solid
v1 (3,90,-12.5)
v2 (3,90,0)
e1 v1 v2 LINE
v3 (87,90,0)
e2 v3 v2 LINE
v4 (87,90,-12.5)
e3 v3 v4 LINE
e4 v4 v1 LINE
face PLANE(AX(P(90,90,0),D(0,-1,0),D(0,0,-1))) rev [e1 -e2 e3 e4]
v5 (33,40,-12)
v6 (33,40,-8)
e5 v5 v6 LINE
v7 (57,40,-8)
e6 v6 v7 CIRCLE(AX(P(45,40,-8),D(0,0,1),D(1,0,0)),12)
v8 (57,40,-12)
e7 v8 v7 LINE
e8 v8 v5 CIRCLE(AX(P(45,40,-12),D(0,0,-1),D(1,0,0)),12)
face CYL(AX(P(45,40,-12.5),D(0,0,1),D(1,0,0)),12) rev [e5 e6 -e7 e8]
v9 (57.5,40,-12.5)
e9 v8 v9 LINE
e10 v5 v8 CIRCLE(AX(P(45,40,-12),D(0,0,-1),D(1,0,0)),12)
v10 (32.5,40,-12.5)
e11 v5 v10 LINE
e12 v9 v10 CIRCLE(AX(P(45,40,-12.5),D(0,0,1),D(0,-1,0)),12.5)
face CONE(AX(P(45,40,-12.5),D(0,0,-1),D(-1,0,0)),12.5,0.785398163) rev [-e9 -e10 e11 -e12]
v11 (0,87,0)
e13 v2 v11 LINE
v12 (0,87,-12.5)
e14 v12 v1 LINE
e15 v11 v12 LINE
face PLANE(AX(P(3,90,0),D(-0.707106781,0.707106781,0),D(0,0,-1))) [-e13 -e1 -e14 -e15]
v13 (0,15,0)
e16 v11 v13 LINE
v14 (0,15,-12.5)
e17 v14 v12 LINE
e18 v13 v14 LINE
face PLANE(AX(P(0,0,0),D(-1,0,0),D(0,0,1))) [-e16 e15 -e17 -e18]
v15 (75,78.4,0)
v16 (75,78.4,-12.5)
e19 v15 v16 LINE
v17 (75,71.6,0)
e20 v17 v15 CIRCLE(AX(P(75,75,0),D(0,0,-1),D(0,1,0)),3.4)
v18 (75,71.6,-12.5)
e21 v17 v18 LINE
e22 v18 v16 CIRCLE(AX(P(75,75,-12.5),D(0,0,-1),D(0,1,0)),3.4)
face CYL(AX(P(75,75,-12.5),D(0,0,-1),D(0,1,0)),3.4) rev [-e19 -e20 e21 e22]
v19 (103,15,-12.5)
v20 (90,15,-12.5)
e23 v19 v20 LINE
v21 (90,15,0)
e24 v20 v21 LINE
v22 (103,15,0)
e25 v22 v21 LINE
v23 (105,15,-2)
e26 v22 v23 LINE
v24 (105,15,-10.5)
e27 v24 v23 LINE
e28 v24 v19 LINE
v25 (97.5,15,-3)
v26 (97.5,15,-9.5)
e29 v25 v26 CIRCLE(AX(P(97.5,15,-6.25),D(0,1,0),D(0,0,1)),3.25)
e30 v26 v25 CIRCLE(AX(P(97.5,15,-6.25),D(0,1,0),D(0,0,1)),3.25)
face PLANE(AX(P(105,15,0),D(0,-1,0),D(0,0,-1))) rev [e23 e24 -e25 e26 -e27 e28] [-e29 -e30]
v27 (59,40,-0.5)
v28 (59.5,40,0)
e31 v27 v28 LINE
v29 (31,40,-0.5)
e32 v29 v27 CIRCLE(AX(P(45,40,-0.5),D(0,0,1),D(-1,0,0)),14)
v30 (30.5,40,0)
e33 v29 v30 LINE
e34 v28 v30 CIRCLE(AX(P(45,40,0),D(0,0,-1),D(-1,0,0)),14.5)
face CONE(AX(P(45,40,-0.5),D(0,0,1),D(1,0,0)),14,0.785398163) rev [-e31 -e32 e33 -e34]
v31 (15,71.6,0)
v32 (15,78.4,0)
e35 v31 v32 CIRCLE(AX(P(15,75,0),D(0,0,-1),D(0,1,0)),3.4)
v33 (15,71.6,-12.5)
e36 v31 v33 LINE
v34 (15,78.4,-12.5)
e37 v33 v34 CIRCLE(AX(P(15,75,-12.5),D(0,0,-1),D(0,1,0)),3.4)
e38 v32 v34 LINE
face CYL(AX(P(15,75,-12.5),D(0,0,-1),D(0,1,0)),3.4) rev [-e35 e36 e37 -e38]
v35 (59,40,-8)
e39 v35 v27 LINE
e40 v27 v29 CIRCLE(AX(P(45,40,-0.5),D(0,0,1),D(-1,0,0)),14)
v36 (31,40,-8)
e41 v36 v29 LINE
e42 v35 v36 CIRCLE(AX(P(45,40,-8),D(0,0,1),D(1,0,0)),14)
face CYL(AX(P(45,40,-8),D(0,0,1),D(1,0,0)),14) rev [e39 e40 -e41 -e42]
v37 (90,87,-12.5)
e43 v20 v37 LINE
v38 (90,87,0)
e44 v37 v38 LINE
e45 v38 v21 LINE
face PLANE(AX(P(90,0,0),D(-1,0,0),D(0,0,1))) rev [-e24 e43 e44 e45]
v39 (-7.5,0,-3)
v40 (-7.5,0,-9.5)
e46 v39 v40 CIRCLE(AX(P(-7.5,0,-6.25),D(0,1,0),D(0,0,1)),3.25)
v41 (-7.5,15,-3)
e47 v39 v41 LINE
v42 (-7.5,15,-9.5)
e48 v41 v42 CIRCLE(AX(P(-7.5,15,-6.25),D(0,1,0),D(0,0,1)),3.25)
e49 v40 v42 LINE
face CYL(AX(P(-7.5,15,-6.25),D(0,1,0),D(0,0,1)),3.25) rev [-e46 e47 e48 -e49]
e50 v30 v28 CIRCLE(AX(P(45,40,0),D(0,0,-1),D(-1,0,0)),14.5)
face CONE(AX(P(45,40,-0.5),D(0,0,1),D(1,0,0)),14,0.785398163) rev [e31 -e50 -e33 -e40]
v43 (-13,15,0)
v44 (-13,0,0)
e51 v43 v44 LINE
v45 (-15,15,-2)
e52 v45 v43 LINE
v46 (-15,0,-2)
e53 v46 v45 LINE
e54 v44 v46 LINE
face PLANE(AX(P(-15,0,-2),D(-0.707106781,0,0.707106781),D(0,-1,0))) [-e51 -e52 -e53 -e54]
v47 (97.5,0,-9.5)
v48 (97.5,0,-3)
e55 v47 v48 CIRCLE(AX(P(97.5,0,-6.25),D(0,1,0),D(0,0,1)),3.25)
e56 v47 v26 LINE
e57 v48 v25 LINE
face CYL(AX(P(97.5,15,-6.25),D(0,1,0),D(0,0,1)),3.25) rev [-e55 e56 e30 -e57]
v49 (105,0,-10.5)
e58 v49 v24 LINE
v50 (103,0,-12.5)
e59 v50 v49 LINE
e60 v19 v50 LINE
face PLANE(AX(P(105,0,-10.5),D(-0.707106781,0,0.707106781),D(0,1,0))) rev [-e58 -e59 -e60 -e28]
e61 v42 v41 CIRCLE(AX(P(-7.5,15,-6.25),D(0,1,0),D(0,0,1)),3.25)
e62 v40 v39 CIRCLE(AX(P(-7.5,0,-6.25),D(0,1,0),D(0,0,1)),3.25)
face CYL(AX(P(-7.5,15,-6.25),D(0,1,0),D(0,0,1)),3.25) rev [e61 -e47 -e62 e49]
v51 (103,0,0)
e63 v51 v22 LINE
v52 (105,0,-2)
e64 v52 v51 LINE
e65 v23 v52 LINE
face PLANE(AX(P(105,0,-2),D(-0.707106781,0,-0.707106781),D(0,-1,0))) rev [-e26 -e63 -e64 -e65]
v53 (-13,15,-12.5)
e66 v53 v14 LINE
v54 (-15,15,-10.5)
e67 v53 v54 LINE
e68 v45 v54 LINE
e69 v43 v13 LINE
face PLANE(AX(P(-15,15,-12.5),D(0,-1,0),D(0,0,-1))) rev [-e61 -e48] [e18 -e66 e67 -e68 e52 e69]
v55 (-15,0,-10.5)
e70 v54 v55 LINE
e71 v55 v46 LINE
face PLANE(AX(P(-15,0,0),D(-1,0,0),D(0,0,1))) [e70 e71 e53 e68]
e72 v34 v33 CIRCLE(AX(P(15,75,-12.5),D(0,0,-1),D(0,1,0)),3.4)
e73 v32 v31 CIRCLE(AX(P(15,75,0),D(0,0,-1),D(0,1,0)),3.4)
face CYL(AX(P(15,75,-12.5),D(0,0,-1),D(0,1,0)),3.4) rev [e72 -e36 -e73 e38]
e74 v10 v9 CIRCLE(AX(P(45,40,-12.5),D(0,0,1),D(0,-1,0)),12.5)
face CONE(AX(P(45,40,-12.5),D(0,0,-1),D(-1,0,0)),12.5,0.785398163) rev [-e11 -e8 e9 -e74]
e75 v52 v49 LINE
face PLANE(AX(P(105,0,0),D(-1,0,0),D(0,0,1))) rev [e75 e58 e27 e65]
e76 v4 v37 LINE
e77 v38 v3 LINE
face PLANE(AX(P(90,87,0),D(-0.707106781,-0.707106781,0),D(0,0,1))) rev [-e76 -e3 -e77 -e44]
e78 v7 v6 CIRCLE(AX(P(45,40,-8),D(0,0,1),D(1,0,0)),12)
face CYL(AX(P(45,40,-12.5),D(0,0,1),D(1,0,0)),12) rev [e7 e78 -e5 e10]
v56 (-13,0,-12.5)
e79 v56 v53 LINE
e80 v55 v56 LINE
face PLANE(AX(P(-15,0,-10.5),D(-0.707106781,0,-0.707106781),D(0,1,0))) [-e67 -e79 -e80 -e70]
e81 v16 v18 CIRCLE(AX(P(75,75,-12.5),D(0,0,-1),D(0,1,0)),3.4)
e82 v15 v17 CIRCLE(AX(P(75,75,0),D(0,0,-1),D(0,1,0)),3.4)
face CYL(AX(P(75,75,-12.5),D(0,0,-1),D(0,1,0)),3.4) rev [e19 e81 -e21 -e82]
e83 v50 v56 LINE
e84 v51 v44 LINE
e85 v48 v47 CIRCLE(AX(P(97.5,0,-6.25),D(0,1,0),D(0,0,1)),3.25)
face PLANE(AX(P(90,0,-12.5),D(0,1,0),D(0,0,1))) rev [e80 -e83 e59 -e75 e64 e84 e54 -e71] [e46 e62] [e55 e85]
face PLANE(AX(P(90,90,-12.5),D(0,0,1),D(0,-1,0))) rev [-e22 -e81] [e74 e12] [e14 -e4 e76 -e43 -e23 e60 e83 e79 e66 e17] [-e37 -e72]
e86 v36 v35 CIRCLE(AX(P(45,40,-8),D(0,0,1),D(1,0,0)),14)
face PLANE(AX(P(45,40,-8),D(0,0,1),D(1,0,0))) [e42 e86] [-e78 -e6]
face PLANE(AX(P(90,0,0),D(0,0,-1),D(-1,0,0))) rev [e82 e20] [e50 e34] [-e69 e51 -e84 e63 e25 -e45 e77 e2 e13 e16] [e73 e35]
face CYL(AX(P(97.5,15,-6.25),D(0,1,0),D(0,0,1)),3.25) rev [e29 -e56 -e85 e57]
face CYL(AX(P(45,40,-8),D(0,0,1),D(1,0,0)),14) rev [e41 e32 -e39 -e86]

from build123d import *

# Parameters (mm, degrees)
SKETCH_1_W              = 12.5
SKETCH_1_H              = 90
EXTRUDE_1_DEPTH         = 90
CHAMFER_1_SIZE          = 3
HOLE_WIZARD_M8_1_D      = 6.8
SKETCH_6_R              = 14
CUT_EXTRUDE_1_DEPTH     = 8
SKETCH_7_R              = 12
CUT_EXTRUDE_2_DEPTH     = 128.530388535
CHAMFER_2_SIZE          = 0.5
SKETCH_10_W             = 12.5
SKETCH_10_H             = 15
EXTRUDE_3_DEPTH         = 15
SKETCH_11_W             = 12.5
SKETCH_11_H             = 15
EXTRUDE_4_DEPTH         = 15
CHAMFER_4_SIZE          = 2
HOLE_WIZARD_6_5_6_5_1_D = 6.5


with BuildPart() as part:
    # 草图1 → 凸台-拉伸1 (new body)
    with BuildSketch(Plane(origin=(0, 0, 0), x_dir=(0, 0, -1), z_dir=(1, 0, 0))):
        with Locations((6.25, 45)):
            Rectangle(SKETCH_1_W, SKETCH_1_H)
    extrude(amount=EXTRUDE_1_DEPTH)

    # 倒角1
    chamfer_1_edges = [part.edges().sort_by_distance(p)[0] for p in [
        (90, 90, -6.25),
        (0, 90, -6.25),
    ]]
    chamfer(chamfer_1_edges, length=CHAMFER_1_SIZE)

    # M8 螺纹孔1 (through all)
    with Locations(Plane(origin=(0, 0, -12.5), x_dir=(-1, 0, 0), z_dir=(0, 0, -1))):
        with Locations((-15, 75), (-75, 75)):
            Hole(HOLE_WIZARD_M8_1_D / 2)

    # 草图6 → 切除-拉伸1 (cut)
    with BuildSketch(Plane.XY):
        with Locations((45, 40)):
            Circle(SKETCH_6_R)
    extrude(amount=-CUT_EXTRUDE_1_DEPTH, mode=Mode.SUBTRACT)

    # 草图7 → 切除-拉伸2 (cut, through all)
    with BuildSketch(Plane.XY.offset(-8)):
        with Locations((45, 40)):
            Circle(SKETCH_7_R)
    extrude(amount=-CUT_EXTRUDE_2_DEPTH, mode=Mode.SUBTRACT)

    # 倒角2
    chamfer_2_edges = [part.edges().sort_by_distance(p)[0] for p in [
        (31, 40, 0),
        (33, 40, -12.5),
    ]]
    chamfer(chamfer_2_edges, length=CHAMFER_2_SIZE)

    # 草图10 → 凸台-拉伸3 (add)
    with BuildSketch(Plane(origin=(90, 0, 0), x_dir=(0, 0, -1), z_dir=(1, 0, 0))):
        with Locations((6.25, 7.5)):
            Rectangle(SKETCH_10_W, SKETCH_10_H)
    extrude(amount=EXTRUDE_3_DEPTH)

    # 草图11 → 凸台-拉伸4 (add)
    with BuildSketch(Plane.ZY):
        with Locations((-6.25, 7.5)):
            Rectangle(SKETCH_11_W, SKETCH_11_H)
    extrude(amount=EXTRUDE_4_DEPTH)

    # 倒角4
    chamfer_4_edges = [part.edges().sort_by_distance(p)[0] for p in [
        (105, 7.5, 0),
        (-15, 7.5, 0),
        (-15, 7.5, -12.5),
        (105, 7.5, -12.5),
    ]]
    chamfer(chamfer_4_edges, length=CHAMFER_4_SIZE)

    # Ø6.5 (6.5) 直径孔1 (through all)
    with Locations(Plane(origin=(-61.758148559, 15, 1.949959902), x_dir=(1, 0, 0), z_dir=(0, 1, 0))):
        with Locations((159.258148559, 8.199959902), (54.258148559, 8.199959902)):
            Hole(HOLE_WIZARD_6_5_6_5_1_D / 2)


solid = part.part
